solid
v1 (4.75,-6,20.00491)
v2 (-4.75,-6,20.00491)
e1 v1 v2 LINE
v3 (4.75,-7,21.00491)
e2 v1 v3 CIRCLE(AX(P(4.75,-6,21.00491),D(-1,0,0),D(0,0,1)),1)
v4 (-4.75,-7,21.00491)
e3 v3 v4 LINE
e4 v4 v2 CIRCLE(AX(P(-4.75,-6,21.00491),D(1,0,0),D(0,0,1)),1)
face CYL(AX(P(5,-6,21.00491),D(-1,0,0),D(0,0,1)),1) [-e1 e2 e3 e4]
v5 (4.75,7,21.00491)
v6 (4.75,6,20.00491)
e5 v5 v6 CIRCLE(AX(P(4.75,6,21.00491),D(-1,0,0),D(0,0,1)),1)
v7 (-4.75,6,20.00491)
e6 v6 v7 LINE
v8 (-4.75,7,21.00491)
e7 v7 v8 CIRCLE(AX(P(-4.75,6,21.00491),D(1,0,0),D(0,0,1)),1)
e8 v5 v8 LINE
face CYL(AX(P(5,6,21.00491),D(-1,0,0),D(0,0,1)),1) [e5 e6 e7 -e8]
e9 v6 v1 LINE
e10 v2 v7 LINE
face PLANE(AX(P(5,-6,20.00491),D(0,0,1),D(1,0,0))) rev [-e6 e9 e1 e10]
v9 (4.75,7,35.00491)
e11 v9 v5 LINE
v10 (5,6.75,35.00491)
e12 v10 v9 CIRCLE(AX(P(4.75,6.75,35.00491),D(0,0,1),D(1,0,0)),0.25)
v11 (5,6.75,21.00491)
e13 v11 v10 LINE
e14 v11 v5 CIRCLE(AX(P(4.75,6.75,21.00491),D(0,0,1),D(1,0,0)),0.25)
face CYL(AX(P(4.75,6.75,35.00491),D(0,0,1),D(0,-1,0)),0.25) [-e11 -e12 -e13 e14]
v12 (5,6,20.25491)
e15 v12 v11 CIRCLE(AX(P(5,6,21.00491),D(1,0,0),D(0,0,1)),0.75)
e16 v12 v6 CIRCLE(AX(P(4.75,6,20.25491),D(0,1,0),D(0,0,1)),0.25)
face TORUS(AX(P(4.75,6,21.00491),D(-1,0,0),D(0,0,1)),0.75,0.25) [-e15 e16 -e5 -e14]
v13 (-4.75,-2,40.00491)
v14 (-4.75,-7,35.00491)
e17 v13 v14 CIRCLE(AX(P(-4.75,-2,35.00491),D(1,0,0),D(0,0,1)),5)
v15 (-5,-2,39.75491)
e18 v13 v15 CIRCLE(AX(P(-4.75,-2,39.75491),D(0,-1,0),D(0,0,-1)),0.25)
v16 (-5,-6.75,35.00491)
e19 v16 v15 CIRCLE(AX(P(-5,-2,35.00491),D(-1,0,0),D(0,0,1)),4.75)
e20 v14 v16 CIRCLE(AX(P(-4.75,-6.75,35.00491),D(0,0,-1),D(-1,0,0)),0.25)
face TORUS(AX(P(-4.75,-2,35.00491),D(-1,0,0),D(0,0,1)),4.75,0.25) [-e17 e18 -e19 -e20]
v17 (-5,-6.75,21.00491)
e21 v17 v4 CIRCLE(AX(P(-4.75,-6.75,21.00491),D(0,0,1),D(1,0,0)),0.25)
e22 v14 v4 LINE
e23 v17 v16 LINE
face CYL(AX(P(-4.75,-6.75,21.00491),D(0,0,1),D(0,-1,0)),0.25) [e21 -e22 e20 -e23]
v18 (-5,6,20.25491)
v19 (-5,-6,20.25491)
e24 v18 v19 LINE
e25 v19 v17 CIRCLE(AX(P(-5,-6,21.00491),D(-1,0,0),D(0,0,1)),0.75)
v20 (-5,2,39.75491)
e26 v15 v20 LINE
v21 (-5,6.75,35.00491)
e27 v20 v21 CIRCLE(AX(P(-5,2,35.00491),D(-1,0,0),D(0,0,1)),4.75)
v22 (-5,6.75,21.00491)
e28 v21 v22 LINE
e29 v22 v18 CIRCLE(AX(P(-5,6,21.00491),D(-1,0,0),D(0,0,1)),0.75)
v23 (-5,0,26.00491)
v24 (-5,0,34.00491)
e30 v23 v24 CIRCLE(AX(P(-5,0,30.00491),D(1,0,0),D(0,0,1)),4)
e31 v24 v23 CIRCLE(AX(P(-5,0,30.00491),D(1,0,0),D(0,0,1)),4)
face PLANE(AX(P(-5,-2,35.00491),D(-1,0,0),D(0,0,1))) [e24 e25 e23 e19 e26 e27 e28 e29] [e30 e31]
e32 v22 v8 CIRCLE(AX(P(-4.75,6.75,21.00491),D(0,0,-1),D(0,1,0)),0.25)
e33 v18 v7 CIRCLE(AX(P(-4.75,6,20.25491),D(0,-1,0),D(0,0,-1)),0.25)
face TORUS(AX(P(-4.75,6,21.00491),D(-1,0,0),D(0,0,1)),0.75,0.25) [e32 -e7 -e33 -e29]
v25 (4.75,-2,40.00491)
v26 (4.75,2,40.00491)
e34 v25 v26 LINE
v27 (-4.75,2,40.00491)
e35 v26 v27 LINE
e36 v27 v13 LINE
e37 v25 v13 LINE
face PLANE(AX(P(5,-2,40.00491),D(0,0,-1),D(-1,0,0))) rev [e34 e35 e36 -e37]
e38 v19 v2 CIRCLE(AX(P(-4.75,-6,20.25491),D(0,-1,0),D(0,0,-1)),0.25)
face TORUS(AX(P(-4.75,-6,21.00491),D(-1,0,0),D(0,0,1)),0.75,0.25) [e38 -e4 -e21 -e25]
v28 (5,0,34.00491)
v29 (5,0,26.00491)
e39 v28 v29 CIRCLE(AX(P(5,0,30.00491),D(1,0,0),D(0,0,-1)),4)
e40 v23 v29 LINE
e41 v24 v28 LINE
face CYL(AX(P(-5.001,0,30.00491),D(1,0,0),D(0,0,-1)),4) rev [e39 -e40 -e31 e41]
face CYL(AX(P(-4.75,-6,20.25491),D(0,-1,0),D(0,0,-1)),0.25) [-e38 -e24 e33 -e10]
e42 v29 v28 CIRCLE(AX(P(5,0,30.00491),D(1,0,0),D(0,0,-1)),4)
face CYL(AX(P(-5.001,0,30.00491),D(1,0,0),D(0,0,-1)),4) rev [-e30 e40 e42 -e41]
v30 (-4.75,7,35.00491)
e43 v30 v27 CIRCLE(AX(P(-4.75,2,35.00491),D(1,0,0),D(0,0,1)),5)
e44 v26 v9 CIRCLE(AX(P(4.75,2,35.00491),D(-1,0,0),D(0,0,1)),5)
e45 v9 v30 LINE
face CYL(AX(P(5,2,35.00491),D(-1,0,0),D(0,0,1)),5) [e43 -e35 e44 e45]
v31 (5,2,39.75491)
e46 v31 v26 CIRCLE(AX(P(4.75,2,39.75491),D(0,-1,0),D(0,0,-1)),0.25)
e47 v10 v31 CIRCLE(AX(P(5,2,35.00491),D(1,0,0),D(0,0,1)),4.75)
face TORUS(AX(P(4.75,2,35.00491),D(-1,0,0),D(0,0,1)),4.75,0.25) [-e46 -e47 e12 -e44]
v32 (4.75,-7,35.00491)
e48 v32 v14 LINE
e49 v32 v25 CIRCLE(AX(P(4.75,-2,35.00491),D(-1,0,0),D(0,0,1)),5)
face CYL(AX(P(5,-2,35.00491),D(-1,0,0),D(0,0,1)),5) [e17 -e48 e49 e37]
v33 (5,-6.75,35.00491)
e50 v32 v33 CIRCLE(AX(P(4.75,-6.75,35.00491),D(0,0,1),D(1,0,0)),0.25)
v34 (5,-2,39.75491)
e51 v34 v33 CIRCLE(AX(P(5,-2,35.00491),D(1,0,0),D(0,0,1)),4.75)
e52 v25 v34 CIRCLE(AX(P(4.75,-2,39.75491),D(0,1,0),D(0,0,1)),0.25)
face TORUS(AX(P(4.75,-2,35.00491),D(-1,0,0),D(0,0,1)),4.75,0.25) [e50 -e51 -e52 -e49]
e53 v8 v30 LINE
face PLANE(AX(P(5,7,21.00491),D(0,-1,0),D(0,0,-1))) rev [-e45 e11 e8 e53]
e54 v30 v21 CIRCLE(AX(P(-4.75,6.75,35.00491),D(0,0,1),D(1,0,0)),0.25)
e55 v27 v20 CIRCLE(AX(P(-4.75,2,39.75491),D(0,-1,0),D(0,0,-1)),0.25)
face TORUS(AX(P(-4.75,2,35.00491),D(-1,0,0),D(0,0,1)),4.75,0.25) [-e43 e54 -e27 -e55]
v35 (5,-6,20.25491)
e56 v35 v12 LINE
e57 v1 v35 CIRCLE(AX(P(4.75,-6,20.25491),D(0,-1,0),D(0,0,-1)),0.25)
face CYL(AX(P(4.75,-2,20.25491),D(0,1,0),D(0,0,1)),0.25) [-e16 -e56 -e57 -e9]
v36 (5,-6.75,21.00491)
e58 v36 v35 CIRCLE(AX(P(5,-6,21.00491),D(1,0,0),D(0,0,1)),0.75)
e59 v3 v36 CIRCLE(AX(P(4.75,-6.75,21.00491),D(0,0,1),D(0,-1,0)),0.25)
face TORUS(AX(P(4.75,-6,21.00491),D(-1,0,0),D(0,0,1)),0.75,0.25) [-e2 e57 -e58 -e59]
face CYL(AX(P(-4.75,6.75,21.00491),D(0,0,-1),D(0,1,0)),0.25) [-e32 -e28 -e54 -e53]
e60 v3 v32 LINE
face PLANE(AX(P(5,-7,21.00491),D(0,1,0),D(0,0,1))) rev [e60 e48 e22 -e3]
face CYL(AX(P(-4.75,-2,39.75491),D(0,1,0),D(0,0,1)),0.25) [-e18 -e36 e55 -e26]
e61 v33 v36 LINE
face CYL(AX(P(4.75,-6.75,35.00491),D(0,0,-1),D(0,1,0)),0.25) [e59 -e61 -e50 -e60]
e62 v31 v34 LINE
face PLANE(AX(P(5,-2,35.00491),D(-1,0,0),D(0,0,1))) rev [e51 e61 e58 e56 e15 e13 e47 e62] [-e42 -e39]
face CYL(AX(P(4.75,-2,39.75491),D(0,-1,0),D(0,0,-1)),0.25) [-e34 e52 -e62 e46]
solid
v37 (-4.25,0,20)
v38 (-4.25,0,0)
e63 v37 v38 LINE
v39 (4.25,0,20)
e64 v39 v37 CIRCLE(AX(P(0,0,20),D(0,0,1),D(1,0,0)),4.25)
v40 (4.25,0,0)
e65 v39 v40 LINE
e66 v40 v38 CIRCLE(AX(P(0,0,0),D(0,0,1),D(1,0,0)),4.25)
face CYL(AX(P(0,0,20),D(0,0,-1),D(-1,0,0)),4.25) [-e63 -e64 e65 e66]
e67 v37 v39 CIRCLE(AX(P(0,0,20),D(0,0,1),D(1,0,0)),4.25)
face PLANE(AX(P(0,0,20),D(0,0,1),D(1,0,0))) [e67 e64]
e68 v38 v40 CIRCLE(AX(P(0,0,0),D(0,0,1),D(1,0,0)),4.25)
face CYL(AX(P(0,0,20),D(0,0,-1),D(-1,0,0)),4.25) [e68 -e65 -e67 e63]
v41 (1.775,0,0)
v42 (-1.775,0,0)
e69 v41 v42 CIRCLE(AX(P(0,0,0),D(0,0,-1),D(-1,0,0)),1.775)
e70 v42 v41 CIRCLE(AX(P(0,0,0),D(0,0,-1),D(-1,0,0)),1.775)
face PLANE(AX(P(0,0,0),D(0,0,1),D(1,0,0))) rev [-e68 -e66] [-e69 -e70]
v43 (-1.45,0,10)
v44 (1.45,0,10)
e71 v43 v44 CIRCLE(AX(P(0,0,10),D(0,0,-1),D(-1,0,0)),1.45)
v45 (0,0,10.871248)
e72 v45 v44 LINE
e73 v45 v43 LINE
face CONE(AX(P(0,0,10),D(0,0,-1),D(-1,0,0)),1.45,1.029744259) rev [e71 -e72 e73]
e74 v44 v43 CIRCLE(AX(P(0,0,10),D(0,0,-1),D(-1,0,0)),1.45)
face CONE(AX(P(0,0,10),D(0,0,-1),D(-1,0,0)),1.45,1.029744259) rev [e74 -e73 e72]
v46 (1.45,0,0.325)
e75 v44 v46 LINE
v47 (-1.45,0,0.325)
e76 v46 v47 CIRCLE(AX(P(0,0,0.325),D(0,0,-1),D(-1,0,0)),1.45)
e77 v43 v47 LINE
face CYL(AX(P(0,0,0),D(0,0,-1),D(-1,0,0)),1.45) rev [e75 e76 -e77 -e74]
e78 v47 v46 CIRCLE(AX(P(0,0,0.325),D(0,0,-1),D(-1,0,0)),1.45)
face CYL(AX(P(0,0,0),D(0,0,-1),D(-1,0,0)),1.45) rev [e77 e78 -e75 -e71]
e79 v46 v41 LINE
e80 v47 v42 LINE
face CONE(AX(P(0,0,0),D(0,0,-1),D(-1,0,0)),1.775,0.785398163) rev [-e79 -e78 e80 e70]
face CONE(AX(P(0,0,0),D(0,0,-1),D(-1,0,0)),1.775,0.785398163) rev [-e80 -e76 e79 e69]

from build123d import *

# Parameters (mm, degrees)
SKETCH1_R           = 4.25
BOSS_EXTRUDE1_DEPTH = 20
BOSS_EXTRUDE2_DEPTH = 5
FILLET1_R           = 0.25
SKETCH5_R           = 4
CUT_EXTRUDE1_DEPTH  = 10


with BuildPart() as part:
    # Sketch1 → Boss-Extrude1 (new body)
    with BuildSketch(Plane.XY):
        Circle(SKETCH1_R)
    extrude(amount=BOSS_EXTRUDE1_DEPTH)

    # Sketch4 → M3.5 Tapped Hole1 (revolve, cut)
    with BuildSketch(Plane.YZ):
        Polygon((0, 0), (0, 10.871247898), (1.45, 10), (1.45, 0.325), (1.775, 0), align=None)
    revolve(axis=Axis((0, 0, -6.35), (0, 0, 1)), mode=Mode.SUBTRACT)


with BuildPart() as body_2:
    # Sketch2 → Boss-Extrude2 (new, symmetric)
    with BuildSketch(Plane(origin=(0, 0, 0), x_dir=(0, 0, -1), z_dir=(1, 0, 0))):
        with BuildLine():
            Line((-21.004909906, -7), (-35.004909906, -7))
            ThreePointArc((-35.004909906, -7), (-38.540443812, -5.535533906), (-40.004909906, -2))
            Line((-40.004909906, -2), (-40.004909906, 2))
            ThreePointArc((-40.004909906, 2), (-38.540443812, 5.535533906), (-35.004909906, 7))
            Line((-35.004909906, 7), (-21.004909906, 7))
            ThreePointArc((-21.004909906, 7), (-20.297803125, 6.707106781), (-20.004909906, 6))
            Line((-20.004909906, 6), (-20.004909906, -6))
            ThreePointArc((-20.004909906, -6), (-20.297803125, -6.707106781), (-21.004909906, -7))
        make_face()
    extrude(amount=BOSS_EXTRUDE2_DEPTH, both=True)

    # Fillet1
    fillet1_edges = [body_2.edges().sort_by_distance(p)[0] for p in [
        (-5, 0, 20.004909906),
        (-5, -6.707106781, 20.297803125),
        (-5, -7, 28.004909906),
        (-5, -5.535533906, 38.540443812),
        (5, -6.707106781, 20.297803125),
        (5, 0, 20.004909906),
        (5, 6.707106781, 20.297803125),
        (5, 7, 28.004909906),
        (5, 5.535533906, 38.540443812),
        (5, 0, 40.004909906),
        (5, -5.535533906, 38.540443812),
        (-5, 0, 40.004909906),
        (5, -7, 28.004909906),
        (-5, 5.535533906, 38.540443812),
        (-5, 7, 28.004909906),
        (-5, 6.707106781, 20.297803125),
    ]]
    fillet(fillet1_edges, radius=FILLET1_R)

    # Sketch5 → Cut-Extrude1 (cut)
    with BuildSketch(Plane(origin=(5, 0, 0), x_dir=(0, 0, -1), z_dir=(1, 0, 0))):
        with Locations((-30.004909906, 0)):
            Circle(SKETCH5_R)
    extrude(amount=-CUT_EXTRUDE1_DEPTH, mode=Mode.SUBTRACT)


solid = Compound([part.part, body_2.part])
